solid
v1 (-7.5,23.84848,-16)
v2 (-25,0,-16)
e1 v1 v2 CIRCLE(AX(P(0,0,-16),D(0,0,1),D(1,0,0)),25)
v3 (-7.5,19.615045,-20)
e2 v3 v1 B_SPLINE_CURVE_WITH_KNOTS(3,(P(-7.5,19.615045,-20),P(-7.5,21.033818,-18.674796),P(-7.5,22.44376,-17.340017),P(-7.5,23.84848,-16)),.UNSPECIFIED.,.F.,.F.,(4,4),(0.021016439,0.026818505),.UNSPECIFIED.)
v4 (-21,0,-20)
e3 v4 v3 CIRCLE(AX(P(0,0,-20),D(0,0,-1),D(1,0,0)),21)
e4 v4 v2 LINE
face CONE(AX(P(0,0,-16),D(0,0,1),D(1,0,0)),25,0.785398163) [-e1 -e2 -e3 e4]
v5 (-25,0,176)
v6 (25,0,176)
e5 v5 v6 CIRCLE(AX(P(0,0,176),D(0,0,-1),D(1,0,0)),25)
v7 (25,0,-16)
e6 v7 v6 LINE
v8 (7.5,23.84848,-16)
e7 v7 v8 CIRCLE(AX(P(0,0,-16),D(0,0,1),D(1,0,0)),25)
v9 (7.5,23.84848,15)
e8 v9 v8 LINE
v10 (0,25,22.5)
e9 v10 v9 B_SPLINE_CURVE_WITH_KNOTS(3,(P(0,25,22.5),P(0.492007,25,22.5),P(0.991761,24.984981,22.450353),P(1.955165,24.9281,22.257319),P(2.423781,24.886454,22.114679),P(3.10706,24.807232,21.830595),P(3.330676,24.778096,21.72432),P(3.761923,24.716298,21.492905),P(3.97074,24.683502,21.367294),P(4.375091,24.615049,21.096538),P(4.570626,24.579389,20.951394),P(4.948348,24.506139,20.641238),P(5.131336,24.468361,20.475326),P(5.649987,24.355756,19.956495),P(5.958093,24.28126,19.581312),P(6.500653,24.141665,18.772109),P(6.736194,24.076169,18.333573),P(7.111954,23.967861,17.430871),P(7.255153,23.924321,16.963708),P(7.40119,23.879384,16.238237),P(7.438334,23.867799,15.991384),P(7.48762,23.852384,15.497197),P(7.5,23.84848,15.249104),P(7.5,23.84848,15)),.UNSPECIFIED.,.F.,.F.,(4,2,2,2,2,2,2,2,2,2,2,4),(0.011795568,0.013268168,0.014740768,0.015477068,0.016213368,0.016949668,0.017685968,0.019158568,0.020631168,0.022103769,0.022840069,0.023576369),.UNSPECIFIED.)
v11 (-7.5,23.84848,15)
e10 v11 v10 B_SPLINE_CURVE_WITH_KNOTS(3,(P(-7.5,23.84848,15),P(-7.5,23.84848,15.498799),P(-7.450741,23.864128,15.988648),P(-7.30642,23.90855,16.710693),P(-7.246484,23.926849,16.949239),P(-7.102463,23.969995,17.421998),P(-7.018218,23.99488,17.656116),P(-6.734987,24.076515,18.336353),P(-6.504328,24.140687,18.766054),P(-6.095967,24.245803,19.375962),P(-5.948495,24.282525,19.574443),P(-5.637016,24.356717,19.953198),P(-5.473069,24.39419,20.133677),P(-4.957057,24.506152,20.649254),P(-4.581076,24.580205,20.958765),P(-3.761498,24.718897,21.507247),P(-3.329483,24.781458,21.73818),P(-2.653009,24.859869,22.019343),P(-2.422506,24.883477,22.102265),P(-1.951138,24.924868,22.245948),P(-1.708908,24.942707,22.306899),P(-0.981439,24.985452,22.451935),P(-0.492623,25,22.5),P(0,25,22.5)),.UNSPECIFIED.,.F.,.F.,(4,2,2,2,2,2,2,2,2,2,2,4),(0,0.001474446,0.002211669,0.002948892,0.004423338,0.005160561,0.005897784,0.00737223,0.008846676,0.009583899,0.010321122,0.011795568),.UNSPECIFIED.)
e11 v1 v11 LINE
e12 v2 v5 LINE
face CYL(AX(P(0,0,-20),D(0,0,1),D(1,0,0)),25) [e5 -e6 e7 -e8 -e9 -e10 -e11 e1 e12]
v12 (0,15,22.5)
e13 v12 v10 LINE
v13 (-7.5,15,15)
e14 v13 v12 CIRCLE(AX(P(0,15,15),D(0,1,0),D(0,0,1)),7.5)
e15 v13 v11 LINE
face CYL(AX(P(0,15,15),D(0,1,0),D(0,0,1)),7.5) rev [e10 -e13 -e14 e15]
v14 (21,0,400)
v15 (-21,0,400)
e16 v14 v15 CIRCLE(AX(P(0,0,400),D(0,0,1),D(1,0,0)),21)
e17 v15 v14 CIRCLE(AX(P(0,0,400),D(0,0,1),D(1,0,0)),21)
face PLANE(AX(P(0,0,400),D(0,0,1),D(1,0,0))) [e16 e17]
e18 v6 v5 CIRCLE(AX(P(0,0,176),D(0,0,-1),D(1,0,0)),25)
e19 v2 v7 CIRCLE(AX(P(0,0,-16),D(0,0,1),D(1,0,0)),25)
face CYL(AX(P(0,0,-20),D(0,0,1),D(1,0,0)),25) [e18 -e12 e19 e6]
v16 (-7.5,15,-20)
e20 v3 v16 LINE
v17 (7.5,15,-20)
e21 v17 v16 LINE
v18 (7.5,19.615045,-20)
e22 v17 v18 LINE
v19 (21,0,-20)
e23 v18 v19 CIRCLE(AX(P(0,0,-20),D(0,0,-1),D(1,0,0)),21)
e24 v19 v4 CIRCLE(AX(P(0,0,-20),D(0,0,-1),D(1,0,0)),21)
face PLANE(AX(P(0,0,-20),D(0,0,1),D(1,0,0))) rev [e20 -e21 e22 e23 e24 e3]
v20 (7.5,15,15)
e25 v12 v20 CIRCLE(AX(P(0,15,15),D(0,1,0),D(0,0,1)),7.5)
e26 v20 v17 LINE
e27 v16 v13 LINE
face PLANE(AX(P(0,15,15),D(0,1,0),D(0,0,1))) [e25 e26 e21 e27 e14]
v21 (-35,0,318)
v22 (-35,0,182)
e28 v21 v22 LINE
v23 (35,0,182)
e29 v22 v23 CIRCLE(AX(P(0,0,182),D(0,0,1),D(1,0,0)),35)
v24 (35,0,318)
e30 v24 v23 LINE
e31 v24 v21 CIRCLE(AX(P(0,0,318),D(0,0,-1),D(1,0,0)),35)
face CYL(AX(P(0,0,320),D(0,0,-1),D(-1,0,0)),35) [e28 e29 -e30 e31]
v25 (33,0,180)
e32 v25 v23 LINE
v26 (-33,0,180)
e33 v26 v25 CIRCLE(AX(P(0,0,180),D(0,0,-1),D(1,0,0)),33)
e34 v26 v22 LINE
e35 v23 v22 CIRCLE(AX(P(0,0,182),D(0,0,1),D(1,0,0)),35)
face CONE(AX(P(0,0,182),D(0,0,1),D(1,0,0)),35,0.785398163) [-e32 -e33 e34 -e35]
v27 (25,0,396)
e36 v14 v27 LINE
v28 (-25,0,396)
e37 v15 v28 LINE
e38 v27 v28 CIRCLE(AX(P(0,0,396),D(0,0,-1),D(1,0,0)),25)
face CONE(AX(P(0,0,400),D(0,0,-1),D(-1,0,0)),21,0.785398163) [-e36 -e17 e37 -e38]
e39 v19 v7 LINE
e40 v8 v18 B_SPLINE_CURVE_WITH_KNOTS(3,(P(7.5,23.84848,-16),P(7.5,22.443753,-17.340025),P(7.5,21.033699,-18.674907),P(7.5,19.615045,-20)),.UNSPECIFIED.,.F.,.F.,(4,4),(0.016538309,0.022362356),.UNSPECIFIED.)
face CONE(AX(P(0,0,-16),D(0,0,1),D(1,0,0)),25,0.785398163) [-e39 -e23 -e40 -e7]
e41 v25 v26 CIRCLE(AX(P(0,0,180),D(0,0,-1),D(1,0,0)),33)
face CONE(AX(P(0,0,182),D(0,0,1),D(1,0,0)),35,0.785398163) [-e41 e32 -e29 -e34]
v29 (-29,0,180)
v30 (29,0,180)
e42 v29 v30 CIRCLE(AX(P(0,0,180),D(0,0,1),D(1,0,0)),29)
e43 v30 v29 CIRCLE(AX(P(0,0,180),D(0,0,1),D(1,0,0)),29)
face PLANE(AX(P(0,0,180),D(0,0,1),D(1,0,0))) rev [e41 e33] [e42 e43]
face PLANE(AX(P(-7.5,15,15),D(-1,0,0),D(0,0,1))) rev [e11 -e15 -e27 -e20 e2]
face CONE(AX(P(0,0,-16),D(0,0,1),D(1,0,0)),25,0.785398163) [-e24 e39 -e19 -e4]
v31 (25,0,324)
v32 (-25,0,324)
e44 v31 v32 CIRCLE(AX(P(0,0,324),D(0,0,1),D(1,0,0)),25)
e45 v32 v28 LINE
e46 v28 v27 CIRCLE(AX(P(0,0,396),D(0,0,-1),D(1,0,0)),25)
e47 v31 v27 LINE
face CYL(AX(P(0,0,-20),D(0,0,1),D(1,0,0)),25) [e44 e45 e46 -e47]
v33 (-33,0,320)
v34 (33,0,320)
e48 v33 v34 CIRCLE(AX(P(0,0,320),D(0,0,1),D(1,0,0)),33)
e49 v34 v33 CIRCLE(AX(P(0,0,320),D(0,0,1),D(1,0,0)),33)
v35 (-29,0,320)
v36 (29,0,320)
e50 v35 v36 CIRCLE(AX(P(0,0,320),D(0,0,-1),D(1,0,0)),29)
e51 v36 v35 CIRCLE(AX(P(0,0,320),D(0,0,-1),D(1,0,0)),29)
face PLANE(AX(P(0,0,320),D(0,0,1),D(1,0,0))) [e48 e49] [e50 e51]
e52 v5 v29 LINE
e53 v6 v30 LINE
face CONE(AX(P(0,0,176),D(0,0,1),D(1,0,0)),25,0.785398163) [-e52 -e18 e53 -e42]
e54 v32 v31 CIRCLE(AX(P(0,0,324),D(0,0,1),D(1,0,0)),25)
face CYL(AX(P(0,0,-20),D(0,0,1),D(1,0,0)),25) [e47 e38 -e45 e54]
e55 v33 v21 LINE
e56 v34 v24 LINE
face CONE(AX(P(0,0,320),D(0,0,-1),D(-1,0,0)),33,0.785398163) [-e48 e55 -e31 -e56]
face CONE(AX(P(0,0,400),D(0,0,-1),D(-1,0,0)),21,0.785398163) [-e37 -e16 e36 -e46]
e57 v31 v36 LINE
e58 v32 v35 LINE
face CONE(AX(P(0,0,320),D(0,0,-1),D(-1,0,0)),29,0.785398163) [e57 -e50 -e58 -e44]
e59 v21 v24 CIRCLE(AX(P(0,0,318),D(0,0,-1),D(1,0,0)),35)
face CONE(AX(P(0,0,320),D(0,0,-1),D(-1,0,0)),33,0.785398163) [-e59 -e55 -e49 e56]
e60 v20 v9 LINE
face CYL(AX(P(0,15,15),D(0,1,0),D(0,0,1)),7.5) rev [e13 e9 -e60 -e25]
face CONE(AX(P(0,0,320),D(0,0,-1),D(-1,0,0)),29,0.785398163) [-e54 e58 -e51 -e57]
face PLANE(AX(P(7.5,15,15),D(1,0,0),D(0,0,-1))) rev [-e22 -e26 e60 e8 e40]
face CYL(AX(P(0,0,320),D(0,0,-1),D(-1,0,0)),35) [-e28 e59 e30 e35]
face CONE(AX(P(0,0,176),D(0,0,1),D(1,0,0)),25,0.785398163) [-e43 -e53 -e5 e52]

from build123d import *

# Parameters (mm, degrees)
BOSS_EXTRUDE1_DEPTH      = 400
BOSS_EXTRUDE1_DEPTH_BACK = 20
SKETCH1_R                = 25
CHAMFER1_SIZE            = 4
CUT_EXTRUDE1_DEPTH       = 10
SKETCH3_R                = 35
BOSS_EXTRUDE2_DEPTH      = 70
CHAMFER2_SIZE            = 2
CHAMFER3_SIZE            = 4


with BuildPart() as part:
    # Sketch1 → Boss-Extrude1 (new, two sides: drawn at the far end of the back side and taken through both)
    with BuildSketch(Plane.XY.offset(-BOSS_EXTRUDE1_DEPTH_BACK)):
        Circle(SKETCH1_R)
    extrude(amount=BOSS_EXTRUDE1_DEPTH + BOSS_EXTRUDE1_DEPTH_BACK)

    # Chamfer1
    chamfer1_edges = [part.edges().sort_by_distance(p)[0] for p in [
        (-25, 0, -20),
        (-25, 0, 400),
    ]]
    chamfer(chamfer1_edges, length=CHAMFER1_SIZE)

    # Sketch2 → Cut-Extrude1 (cut)
    with BuildSketch(Plane(origin=(0, 25, 0), x_dir=(1, 0, 0), z_dir=(0, 1, 0))):
        with BuildLine():
            Line((7.5, -15), (7.5, 55))
            Line((7.5, 55), (-7.5, 55))
            Line((-7.5, 55), (-7.5, -15))
            ThreePointArc((-7.5, -15), (0, -22.5), (7.5, -15))
        make_face()
    extrude(amount=-CUT_EXTRUDE1_DEPTH, mode=Mode.SUBTRACT)

    # Sketch3 → Boss-Extrude2 (add, symmetric)
    with BuildSketch(Plane.XY.offset(250)):
        Circle(SKETCH3_R)
    extrude(amount=BOSS_EXTRUDE2_DEPTH, both=True)

    # Chamfer2
    chamfer2_edges = [part.edges().sort_by_distance(p)[0] for p in [
        (-35, 0, 180),
        (-35, 0, 320),
    ]]
    chamfer(chamfer2_edges, length=CHAMFER2_SIZE)

    # Chamfer3
    chamfer3_edges = [part.edges().sort_by_distance(p)[0] for p in [
        (-25, 0, 320),
        (-25, 0, 180),
    ]]
    chamfer(chamfer3_edges, length=CHAMFER3_SIZE)


solid = part.part
